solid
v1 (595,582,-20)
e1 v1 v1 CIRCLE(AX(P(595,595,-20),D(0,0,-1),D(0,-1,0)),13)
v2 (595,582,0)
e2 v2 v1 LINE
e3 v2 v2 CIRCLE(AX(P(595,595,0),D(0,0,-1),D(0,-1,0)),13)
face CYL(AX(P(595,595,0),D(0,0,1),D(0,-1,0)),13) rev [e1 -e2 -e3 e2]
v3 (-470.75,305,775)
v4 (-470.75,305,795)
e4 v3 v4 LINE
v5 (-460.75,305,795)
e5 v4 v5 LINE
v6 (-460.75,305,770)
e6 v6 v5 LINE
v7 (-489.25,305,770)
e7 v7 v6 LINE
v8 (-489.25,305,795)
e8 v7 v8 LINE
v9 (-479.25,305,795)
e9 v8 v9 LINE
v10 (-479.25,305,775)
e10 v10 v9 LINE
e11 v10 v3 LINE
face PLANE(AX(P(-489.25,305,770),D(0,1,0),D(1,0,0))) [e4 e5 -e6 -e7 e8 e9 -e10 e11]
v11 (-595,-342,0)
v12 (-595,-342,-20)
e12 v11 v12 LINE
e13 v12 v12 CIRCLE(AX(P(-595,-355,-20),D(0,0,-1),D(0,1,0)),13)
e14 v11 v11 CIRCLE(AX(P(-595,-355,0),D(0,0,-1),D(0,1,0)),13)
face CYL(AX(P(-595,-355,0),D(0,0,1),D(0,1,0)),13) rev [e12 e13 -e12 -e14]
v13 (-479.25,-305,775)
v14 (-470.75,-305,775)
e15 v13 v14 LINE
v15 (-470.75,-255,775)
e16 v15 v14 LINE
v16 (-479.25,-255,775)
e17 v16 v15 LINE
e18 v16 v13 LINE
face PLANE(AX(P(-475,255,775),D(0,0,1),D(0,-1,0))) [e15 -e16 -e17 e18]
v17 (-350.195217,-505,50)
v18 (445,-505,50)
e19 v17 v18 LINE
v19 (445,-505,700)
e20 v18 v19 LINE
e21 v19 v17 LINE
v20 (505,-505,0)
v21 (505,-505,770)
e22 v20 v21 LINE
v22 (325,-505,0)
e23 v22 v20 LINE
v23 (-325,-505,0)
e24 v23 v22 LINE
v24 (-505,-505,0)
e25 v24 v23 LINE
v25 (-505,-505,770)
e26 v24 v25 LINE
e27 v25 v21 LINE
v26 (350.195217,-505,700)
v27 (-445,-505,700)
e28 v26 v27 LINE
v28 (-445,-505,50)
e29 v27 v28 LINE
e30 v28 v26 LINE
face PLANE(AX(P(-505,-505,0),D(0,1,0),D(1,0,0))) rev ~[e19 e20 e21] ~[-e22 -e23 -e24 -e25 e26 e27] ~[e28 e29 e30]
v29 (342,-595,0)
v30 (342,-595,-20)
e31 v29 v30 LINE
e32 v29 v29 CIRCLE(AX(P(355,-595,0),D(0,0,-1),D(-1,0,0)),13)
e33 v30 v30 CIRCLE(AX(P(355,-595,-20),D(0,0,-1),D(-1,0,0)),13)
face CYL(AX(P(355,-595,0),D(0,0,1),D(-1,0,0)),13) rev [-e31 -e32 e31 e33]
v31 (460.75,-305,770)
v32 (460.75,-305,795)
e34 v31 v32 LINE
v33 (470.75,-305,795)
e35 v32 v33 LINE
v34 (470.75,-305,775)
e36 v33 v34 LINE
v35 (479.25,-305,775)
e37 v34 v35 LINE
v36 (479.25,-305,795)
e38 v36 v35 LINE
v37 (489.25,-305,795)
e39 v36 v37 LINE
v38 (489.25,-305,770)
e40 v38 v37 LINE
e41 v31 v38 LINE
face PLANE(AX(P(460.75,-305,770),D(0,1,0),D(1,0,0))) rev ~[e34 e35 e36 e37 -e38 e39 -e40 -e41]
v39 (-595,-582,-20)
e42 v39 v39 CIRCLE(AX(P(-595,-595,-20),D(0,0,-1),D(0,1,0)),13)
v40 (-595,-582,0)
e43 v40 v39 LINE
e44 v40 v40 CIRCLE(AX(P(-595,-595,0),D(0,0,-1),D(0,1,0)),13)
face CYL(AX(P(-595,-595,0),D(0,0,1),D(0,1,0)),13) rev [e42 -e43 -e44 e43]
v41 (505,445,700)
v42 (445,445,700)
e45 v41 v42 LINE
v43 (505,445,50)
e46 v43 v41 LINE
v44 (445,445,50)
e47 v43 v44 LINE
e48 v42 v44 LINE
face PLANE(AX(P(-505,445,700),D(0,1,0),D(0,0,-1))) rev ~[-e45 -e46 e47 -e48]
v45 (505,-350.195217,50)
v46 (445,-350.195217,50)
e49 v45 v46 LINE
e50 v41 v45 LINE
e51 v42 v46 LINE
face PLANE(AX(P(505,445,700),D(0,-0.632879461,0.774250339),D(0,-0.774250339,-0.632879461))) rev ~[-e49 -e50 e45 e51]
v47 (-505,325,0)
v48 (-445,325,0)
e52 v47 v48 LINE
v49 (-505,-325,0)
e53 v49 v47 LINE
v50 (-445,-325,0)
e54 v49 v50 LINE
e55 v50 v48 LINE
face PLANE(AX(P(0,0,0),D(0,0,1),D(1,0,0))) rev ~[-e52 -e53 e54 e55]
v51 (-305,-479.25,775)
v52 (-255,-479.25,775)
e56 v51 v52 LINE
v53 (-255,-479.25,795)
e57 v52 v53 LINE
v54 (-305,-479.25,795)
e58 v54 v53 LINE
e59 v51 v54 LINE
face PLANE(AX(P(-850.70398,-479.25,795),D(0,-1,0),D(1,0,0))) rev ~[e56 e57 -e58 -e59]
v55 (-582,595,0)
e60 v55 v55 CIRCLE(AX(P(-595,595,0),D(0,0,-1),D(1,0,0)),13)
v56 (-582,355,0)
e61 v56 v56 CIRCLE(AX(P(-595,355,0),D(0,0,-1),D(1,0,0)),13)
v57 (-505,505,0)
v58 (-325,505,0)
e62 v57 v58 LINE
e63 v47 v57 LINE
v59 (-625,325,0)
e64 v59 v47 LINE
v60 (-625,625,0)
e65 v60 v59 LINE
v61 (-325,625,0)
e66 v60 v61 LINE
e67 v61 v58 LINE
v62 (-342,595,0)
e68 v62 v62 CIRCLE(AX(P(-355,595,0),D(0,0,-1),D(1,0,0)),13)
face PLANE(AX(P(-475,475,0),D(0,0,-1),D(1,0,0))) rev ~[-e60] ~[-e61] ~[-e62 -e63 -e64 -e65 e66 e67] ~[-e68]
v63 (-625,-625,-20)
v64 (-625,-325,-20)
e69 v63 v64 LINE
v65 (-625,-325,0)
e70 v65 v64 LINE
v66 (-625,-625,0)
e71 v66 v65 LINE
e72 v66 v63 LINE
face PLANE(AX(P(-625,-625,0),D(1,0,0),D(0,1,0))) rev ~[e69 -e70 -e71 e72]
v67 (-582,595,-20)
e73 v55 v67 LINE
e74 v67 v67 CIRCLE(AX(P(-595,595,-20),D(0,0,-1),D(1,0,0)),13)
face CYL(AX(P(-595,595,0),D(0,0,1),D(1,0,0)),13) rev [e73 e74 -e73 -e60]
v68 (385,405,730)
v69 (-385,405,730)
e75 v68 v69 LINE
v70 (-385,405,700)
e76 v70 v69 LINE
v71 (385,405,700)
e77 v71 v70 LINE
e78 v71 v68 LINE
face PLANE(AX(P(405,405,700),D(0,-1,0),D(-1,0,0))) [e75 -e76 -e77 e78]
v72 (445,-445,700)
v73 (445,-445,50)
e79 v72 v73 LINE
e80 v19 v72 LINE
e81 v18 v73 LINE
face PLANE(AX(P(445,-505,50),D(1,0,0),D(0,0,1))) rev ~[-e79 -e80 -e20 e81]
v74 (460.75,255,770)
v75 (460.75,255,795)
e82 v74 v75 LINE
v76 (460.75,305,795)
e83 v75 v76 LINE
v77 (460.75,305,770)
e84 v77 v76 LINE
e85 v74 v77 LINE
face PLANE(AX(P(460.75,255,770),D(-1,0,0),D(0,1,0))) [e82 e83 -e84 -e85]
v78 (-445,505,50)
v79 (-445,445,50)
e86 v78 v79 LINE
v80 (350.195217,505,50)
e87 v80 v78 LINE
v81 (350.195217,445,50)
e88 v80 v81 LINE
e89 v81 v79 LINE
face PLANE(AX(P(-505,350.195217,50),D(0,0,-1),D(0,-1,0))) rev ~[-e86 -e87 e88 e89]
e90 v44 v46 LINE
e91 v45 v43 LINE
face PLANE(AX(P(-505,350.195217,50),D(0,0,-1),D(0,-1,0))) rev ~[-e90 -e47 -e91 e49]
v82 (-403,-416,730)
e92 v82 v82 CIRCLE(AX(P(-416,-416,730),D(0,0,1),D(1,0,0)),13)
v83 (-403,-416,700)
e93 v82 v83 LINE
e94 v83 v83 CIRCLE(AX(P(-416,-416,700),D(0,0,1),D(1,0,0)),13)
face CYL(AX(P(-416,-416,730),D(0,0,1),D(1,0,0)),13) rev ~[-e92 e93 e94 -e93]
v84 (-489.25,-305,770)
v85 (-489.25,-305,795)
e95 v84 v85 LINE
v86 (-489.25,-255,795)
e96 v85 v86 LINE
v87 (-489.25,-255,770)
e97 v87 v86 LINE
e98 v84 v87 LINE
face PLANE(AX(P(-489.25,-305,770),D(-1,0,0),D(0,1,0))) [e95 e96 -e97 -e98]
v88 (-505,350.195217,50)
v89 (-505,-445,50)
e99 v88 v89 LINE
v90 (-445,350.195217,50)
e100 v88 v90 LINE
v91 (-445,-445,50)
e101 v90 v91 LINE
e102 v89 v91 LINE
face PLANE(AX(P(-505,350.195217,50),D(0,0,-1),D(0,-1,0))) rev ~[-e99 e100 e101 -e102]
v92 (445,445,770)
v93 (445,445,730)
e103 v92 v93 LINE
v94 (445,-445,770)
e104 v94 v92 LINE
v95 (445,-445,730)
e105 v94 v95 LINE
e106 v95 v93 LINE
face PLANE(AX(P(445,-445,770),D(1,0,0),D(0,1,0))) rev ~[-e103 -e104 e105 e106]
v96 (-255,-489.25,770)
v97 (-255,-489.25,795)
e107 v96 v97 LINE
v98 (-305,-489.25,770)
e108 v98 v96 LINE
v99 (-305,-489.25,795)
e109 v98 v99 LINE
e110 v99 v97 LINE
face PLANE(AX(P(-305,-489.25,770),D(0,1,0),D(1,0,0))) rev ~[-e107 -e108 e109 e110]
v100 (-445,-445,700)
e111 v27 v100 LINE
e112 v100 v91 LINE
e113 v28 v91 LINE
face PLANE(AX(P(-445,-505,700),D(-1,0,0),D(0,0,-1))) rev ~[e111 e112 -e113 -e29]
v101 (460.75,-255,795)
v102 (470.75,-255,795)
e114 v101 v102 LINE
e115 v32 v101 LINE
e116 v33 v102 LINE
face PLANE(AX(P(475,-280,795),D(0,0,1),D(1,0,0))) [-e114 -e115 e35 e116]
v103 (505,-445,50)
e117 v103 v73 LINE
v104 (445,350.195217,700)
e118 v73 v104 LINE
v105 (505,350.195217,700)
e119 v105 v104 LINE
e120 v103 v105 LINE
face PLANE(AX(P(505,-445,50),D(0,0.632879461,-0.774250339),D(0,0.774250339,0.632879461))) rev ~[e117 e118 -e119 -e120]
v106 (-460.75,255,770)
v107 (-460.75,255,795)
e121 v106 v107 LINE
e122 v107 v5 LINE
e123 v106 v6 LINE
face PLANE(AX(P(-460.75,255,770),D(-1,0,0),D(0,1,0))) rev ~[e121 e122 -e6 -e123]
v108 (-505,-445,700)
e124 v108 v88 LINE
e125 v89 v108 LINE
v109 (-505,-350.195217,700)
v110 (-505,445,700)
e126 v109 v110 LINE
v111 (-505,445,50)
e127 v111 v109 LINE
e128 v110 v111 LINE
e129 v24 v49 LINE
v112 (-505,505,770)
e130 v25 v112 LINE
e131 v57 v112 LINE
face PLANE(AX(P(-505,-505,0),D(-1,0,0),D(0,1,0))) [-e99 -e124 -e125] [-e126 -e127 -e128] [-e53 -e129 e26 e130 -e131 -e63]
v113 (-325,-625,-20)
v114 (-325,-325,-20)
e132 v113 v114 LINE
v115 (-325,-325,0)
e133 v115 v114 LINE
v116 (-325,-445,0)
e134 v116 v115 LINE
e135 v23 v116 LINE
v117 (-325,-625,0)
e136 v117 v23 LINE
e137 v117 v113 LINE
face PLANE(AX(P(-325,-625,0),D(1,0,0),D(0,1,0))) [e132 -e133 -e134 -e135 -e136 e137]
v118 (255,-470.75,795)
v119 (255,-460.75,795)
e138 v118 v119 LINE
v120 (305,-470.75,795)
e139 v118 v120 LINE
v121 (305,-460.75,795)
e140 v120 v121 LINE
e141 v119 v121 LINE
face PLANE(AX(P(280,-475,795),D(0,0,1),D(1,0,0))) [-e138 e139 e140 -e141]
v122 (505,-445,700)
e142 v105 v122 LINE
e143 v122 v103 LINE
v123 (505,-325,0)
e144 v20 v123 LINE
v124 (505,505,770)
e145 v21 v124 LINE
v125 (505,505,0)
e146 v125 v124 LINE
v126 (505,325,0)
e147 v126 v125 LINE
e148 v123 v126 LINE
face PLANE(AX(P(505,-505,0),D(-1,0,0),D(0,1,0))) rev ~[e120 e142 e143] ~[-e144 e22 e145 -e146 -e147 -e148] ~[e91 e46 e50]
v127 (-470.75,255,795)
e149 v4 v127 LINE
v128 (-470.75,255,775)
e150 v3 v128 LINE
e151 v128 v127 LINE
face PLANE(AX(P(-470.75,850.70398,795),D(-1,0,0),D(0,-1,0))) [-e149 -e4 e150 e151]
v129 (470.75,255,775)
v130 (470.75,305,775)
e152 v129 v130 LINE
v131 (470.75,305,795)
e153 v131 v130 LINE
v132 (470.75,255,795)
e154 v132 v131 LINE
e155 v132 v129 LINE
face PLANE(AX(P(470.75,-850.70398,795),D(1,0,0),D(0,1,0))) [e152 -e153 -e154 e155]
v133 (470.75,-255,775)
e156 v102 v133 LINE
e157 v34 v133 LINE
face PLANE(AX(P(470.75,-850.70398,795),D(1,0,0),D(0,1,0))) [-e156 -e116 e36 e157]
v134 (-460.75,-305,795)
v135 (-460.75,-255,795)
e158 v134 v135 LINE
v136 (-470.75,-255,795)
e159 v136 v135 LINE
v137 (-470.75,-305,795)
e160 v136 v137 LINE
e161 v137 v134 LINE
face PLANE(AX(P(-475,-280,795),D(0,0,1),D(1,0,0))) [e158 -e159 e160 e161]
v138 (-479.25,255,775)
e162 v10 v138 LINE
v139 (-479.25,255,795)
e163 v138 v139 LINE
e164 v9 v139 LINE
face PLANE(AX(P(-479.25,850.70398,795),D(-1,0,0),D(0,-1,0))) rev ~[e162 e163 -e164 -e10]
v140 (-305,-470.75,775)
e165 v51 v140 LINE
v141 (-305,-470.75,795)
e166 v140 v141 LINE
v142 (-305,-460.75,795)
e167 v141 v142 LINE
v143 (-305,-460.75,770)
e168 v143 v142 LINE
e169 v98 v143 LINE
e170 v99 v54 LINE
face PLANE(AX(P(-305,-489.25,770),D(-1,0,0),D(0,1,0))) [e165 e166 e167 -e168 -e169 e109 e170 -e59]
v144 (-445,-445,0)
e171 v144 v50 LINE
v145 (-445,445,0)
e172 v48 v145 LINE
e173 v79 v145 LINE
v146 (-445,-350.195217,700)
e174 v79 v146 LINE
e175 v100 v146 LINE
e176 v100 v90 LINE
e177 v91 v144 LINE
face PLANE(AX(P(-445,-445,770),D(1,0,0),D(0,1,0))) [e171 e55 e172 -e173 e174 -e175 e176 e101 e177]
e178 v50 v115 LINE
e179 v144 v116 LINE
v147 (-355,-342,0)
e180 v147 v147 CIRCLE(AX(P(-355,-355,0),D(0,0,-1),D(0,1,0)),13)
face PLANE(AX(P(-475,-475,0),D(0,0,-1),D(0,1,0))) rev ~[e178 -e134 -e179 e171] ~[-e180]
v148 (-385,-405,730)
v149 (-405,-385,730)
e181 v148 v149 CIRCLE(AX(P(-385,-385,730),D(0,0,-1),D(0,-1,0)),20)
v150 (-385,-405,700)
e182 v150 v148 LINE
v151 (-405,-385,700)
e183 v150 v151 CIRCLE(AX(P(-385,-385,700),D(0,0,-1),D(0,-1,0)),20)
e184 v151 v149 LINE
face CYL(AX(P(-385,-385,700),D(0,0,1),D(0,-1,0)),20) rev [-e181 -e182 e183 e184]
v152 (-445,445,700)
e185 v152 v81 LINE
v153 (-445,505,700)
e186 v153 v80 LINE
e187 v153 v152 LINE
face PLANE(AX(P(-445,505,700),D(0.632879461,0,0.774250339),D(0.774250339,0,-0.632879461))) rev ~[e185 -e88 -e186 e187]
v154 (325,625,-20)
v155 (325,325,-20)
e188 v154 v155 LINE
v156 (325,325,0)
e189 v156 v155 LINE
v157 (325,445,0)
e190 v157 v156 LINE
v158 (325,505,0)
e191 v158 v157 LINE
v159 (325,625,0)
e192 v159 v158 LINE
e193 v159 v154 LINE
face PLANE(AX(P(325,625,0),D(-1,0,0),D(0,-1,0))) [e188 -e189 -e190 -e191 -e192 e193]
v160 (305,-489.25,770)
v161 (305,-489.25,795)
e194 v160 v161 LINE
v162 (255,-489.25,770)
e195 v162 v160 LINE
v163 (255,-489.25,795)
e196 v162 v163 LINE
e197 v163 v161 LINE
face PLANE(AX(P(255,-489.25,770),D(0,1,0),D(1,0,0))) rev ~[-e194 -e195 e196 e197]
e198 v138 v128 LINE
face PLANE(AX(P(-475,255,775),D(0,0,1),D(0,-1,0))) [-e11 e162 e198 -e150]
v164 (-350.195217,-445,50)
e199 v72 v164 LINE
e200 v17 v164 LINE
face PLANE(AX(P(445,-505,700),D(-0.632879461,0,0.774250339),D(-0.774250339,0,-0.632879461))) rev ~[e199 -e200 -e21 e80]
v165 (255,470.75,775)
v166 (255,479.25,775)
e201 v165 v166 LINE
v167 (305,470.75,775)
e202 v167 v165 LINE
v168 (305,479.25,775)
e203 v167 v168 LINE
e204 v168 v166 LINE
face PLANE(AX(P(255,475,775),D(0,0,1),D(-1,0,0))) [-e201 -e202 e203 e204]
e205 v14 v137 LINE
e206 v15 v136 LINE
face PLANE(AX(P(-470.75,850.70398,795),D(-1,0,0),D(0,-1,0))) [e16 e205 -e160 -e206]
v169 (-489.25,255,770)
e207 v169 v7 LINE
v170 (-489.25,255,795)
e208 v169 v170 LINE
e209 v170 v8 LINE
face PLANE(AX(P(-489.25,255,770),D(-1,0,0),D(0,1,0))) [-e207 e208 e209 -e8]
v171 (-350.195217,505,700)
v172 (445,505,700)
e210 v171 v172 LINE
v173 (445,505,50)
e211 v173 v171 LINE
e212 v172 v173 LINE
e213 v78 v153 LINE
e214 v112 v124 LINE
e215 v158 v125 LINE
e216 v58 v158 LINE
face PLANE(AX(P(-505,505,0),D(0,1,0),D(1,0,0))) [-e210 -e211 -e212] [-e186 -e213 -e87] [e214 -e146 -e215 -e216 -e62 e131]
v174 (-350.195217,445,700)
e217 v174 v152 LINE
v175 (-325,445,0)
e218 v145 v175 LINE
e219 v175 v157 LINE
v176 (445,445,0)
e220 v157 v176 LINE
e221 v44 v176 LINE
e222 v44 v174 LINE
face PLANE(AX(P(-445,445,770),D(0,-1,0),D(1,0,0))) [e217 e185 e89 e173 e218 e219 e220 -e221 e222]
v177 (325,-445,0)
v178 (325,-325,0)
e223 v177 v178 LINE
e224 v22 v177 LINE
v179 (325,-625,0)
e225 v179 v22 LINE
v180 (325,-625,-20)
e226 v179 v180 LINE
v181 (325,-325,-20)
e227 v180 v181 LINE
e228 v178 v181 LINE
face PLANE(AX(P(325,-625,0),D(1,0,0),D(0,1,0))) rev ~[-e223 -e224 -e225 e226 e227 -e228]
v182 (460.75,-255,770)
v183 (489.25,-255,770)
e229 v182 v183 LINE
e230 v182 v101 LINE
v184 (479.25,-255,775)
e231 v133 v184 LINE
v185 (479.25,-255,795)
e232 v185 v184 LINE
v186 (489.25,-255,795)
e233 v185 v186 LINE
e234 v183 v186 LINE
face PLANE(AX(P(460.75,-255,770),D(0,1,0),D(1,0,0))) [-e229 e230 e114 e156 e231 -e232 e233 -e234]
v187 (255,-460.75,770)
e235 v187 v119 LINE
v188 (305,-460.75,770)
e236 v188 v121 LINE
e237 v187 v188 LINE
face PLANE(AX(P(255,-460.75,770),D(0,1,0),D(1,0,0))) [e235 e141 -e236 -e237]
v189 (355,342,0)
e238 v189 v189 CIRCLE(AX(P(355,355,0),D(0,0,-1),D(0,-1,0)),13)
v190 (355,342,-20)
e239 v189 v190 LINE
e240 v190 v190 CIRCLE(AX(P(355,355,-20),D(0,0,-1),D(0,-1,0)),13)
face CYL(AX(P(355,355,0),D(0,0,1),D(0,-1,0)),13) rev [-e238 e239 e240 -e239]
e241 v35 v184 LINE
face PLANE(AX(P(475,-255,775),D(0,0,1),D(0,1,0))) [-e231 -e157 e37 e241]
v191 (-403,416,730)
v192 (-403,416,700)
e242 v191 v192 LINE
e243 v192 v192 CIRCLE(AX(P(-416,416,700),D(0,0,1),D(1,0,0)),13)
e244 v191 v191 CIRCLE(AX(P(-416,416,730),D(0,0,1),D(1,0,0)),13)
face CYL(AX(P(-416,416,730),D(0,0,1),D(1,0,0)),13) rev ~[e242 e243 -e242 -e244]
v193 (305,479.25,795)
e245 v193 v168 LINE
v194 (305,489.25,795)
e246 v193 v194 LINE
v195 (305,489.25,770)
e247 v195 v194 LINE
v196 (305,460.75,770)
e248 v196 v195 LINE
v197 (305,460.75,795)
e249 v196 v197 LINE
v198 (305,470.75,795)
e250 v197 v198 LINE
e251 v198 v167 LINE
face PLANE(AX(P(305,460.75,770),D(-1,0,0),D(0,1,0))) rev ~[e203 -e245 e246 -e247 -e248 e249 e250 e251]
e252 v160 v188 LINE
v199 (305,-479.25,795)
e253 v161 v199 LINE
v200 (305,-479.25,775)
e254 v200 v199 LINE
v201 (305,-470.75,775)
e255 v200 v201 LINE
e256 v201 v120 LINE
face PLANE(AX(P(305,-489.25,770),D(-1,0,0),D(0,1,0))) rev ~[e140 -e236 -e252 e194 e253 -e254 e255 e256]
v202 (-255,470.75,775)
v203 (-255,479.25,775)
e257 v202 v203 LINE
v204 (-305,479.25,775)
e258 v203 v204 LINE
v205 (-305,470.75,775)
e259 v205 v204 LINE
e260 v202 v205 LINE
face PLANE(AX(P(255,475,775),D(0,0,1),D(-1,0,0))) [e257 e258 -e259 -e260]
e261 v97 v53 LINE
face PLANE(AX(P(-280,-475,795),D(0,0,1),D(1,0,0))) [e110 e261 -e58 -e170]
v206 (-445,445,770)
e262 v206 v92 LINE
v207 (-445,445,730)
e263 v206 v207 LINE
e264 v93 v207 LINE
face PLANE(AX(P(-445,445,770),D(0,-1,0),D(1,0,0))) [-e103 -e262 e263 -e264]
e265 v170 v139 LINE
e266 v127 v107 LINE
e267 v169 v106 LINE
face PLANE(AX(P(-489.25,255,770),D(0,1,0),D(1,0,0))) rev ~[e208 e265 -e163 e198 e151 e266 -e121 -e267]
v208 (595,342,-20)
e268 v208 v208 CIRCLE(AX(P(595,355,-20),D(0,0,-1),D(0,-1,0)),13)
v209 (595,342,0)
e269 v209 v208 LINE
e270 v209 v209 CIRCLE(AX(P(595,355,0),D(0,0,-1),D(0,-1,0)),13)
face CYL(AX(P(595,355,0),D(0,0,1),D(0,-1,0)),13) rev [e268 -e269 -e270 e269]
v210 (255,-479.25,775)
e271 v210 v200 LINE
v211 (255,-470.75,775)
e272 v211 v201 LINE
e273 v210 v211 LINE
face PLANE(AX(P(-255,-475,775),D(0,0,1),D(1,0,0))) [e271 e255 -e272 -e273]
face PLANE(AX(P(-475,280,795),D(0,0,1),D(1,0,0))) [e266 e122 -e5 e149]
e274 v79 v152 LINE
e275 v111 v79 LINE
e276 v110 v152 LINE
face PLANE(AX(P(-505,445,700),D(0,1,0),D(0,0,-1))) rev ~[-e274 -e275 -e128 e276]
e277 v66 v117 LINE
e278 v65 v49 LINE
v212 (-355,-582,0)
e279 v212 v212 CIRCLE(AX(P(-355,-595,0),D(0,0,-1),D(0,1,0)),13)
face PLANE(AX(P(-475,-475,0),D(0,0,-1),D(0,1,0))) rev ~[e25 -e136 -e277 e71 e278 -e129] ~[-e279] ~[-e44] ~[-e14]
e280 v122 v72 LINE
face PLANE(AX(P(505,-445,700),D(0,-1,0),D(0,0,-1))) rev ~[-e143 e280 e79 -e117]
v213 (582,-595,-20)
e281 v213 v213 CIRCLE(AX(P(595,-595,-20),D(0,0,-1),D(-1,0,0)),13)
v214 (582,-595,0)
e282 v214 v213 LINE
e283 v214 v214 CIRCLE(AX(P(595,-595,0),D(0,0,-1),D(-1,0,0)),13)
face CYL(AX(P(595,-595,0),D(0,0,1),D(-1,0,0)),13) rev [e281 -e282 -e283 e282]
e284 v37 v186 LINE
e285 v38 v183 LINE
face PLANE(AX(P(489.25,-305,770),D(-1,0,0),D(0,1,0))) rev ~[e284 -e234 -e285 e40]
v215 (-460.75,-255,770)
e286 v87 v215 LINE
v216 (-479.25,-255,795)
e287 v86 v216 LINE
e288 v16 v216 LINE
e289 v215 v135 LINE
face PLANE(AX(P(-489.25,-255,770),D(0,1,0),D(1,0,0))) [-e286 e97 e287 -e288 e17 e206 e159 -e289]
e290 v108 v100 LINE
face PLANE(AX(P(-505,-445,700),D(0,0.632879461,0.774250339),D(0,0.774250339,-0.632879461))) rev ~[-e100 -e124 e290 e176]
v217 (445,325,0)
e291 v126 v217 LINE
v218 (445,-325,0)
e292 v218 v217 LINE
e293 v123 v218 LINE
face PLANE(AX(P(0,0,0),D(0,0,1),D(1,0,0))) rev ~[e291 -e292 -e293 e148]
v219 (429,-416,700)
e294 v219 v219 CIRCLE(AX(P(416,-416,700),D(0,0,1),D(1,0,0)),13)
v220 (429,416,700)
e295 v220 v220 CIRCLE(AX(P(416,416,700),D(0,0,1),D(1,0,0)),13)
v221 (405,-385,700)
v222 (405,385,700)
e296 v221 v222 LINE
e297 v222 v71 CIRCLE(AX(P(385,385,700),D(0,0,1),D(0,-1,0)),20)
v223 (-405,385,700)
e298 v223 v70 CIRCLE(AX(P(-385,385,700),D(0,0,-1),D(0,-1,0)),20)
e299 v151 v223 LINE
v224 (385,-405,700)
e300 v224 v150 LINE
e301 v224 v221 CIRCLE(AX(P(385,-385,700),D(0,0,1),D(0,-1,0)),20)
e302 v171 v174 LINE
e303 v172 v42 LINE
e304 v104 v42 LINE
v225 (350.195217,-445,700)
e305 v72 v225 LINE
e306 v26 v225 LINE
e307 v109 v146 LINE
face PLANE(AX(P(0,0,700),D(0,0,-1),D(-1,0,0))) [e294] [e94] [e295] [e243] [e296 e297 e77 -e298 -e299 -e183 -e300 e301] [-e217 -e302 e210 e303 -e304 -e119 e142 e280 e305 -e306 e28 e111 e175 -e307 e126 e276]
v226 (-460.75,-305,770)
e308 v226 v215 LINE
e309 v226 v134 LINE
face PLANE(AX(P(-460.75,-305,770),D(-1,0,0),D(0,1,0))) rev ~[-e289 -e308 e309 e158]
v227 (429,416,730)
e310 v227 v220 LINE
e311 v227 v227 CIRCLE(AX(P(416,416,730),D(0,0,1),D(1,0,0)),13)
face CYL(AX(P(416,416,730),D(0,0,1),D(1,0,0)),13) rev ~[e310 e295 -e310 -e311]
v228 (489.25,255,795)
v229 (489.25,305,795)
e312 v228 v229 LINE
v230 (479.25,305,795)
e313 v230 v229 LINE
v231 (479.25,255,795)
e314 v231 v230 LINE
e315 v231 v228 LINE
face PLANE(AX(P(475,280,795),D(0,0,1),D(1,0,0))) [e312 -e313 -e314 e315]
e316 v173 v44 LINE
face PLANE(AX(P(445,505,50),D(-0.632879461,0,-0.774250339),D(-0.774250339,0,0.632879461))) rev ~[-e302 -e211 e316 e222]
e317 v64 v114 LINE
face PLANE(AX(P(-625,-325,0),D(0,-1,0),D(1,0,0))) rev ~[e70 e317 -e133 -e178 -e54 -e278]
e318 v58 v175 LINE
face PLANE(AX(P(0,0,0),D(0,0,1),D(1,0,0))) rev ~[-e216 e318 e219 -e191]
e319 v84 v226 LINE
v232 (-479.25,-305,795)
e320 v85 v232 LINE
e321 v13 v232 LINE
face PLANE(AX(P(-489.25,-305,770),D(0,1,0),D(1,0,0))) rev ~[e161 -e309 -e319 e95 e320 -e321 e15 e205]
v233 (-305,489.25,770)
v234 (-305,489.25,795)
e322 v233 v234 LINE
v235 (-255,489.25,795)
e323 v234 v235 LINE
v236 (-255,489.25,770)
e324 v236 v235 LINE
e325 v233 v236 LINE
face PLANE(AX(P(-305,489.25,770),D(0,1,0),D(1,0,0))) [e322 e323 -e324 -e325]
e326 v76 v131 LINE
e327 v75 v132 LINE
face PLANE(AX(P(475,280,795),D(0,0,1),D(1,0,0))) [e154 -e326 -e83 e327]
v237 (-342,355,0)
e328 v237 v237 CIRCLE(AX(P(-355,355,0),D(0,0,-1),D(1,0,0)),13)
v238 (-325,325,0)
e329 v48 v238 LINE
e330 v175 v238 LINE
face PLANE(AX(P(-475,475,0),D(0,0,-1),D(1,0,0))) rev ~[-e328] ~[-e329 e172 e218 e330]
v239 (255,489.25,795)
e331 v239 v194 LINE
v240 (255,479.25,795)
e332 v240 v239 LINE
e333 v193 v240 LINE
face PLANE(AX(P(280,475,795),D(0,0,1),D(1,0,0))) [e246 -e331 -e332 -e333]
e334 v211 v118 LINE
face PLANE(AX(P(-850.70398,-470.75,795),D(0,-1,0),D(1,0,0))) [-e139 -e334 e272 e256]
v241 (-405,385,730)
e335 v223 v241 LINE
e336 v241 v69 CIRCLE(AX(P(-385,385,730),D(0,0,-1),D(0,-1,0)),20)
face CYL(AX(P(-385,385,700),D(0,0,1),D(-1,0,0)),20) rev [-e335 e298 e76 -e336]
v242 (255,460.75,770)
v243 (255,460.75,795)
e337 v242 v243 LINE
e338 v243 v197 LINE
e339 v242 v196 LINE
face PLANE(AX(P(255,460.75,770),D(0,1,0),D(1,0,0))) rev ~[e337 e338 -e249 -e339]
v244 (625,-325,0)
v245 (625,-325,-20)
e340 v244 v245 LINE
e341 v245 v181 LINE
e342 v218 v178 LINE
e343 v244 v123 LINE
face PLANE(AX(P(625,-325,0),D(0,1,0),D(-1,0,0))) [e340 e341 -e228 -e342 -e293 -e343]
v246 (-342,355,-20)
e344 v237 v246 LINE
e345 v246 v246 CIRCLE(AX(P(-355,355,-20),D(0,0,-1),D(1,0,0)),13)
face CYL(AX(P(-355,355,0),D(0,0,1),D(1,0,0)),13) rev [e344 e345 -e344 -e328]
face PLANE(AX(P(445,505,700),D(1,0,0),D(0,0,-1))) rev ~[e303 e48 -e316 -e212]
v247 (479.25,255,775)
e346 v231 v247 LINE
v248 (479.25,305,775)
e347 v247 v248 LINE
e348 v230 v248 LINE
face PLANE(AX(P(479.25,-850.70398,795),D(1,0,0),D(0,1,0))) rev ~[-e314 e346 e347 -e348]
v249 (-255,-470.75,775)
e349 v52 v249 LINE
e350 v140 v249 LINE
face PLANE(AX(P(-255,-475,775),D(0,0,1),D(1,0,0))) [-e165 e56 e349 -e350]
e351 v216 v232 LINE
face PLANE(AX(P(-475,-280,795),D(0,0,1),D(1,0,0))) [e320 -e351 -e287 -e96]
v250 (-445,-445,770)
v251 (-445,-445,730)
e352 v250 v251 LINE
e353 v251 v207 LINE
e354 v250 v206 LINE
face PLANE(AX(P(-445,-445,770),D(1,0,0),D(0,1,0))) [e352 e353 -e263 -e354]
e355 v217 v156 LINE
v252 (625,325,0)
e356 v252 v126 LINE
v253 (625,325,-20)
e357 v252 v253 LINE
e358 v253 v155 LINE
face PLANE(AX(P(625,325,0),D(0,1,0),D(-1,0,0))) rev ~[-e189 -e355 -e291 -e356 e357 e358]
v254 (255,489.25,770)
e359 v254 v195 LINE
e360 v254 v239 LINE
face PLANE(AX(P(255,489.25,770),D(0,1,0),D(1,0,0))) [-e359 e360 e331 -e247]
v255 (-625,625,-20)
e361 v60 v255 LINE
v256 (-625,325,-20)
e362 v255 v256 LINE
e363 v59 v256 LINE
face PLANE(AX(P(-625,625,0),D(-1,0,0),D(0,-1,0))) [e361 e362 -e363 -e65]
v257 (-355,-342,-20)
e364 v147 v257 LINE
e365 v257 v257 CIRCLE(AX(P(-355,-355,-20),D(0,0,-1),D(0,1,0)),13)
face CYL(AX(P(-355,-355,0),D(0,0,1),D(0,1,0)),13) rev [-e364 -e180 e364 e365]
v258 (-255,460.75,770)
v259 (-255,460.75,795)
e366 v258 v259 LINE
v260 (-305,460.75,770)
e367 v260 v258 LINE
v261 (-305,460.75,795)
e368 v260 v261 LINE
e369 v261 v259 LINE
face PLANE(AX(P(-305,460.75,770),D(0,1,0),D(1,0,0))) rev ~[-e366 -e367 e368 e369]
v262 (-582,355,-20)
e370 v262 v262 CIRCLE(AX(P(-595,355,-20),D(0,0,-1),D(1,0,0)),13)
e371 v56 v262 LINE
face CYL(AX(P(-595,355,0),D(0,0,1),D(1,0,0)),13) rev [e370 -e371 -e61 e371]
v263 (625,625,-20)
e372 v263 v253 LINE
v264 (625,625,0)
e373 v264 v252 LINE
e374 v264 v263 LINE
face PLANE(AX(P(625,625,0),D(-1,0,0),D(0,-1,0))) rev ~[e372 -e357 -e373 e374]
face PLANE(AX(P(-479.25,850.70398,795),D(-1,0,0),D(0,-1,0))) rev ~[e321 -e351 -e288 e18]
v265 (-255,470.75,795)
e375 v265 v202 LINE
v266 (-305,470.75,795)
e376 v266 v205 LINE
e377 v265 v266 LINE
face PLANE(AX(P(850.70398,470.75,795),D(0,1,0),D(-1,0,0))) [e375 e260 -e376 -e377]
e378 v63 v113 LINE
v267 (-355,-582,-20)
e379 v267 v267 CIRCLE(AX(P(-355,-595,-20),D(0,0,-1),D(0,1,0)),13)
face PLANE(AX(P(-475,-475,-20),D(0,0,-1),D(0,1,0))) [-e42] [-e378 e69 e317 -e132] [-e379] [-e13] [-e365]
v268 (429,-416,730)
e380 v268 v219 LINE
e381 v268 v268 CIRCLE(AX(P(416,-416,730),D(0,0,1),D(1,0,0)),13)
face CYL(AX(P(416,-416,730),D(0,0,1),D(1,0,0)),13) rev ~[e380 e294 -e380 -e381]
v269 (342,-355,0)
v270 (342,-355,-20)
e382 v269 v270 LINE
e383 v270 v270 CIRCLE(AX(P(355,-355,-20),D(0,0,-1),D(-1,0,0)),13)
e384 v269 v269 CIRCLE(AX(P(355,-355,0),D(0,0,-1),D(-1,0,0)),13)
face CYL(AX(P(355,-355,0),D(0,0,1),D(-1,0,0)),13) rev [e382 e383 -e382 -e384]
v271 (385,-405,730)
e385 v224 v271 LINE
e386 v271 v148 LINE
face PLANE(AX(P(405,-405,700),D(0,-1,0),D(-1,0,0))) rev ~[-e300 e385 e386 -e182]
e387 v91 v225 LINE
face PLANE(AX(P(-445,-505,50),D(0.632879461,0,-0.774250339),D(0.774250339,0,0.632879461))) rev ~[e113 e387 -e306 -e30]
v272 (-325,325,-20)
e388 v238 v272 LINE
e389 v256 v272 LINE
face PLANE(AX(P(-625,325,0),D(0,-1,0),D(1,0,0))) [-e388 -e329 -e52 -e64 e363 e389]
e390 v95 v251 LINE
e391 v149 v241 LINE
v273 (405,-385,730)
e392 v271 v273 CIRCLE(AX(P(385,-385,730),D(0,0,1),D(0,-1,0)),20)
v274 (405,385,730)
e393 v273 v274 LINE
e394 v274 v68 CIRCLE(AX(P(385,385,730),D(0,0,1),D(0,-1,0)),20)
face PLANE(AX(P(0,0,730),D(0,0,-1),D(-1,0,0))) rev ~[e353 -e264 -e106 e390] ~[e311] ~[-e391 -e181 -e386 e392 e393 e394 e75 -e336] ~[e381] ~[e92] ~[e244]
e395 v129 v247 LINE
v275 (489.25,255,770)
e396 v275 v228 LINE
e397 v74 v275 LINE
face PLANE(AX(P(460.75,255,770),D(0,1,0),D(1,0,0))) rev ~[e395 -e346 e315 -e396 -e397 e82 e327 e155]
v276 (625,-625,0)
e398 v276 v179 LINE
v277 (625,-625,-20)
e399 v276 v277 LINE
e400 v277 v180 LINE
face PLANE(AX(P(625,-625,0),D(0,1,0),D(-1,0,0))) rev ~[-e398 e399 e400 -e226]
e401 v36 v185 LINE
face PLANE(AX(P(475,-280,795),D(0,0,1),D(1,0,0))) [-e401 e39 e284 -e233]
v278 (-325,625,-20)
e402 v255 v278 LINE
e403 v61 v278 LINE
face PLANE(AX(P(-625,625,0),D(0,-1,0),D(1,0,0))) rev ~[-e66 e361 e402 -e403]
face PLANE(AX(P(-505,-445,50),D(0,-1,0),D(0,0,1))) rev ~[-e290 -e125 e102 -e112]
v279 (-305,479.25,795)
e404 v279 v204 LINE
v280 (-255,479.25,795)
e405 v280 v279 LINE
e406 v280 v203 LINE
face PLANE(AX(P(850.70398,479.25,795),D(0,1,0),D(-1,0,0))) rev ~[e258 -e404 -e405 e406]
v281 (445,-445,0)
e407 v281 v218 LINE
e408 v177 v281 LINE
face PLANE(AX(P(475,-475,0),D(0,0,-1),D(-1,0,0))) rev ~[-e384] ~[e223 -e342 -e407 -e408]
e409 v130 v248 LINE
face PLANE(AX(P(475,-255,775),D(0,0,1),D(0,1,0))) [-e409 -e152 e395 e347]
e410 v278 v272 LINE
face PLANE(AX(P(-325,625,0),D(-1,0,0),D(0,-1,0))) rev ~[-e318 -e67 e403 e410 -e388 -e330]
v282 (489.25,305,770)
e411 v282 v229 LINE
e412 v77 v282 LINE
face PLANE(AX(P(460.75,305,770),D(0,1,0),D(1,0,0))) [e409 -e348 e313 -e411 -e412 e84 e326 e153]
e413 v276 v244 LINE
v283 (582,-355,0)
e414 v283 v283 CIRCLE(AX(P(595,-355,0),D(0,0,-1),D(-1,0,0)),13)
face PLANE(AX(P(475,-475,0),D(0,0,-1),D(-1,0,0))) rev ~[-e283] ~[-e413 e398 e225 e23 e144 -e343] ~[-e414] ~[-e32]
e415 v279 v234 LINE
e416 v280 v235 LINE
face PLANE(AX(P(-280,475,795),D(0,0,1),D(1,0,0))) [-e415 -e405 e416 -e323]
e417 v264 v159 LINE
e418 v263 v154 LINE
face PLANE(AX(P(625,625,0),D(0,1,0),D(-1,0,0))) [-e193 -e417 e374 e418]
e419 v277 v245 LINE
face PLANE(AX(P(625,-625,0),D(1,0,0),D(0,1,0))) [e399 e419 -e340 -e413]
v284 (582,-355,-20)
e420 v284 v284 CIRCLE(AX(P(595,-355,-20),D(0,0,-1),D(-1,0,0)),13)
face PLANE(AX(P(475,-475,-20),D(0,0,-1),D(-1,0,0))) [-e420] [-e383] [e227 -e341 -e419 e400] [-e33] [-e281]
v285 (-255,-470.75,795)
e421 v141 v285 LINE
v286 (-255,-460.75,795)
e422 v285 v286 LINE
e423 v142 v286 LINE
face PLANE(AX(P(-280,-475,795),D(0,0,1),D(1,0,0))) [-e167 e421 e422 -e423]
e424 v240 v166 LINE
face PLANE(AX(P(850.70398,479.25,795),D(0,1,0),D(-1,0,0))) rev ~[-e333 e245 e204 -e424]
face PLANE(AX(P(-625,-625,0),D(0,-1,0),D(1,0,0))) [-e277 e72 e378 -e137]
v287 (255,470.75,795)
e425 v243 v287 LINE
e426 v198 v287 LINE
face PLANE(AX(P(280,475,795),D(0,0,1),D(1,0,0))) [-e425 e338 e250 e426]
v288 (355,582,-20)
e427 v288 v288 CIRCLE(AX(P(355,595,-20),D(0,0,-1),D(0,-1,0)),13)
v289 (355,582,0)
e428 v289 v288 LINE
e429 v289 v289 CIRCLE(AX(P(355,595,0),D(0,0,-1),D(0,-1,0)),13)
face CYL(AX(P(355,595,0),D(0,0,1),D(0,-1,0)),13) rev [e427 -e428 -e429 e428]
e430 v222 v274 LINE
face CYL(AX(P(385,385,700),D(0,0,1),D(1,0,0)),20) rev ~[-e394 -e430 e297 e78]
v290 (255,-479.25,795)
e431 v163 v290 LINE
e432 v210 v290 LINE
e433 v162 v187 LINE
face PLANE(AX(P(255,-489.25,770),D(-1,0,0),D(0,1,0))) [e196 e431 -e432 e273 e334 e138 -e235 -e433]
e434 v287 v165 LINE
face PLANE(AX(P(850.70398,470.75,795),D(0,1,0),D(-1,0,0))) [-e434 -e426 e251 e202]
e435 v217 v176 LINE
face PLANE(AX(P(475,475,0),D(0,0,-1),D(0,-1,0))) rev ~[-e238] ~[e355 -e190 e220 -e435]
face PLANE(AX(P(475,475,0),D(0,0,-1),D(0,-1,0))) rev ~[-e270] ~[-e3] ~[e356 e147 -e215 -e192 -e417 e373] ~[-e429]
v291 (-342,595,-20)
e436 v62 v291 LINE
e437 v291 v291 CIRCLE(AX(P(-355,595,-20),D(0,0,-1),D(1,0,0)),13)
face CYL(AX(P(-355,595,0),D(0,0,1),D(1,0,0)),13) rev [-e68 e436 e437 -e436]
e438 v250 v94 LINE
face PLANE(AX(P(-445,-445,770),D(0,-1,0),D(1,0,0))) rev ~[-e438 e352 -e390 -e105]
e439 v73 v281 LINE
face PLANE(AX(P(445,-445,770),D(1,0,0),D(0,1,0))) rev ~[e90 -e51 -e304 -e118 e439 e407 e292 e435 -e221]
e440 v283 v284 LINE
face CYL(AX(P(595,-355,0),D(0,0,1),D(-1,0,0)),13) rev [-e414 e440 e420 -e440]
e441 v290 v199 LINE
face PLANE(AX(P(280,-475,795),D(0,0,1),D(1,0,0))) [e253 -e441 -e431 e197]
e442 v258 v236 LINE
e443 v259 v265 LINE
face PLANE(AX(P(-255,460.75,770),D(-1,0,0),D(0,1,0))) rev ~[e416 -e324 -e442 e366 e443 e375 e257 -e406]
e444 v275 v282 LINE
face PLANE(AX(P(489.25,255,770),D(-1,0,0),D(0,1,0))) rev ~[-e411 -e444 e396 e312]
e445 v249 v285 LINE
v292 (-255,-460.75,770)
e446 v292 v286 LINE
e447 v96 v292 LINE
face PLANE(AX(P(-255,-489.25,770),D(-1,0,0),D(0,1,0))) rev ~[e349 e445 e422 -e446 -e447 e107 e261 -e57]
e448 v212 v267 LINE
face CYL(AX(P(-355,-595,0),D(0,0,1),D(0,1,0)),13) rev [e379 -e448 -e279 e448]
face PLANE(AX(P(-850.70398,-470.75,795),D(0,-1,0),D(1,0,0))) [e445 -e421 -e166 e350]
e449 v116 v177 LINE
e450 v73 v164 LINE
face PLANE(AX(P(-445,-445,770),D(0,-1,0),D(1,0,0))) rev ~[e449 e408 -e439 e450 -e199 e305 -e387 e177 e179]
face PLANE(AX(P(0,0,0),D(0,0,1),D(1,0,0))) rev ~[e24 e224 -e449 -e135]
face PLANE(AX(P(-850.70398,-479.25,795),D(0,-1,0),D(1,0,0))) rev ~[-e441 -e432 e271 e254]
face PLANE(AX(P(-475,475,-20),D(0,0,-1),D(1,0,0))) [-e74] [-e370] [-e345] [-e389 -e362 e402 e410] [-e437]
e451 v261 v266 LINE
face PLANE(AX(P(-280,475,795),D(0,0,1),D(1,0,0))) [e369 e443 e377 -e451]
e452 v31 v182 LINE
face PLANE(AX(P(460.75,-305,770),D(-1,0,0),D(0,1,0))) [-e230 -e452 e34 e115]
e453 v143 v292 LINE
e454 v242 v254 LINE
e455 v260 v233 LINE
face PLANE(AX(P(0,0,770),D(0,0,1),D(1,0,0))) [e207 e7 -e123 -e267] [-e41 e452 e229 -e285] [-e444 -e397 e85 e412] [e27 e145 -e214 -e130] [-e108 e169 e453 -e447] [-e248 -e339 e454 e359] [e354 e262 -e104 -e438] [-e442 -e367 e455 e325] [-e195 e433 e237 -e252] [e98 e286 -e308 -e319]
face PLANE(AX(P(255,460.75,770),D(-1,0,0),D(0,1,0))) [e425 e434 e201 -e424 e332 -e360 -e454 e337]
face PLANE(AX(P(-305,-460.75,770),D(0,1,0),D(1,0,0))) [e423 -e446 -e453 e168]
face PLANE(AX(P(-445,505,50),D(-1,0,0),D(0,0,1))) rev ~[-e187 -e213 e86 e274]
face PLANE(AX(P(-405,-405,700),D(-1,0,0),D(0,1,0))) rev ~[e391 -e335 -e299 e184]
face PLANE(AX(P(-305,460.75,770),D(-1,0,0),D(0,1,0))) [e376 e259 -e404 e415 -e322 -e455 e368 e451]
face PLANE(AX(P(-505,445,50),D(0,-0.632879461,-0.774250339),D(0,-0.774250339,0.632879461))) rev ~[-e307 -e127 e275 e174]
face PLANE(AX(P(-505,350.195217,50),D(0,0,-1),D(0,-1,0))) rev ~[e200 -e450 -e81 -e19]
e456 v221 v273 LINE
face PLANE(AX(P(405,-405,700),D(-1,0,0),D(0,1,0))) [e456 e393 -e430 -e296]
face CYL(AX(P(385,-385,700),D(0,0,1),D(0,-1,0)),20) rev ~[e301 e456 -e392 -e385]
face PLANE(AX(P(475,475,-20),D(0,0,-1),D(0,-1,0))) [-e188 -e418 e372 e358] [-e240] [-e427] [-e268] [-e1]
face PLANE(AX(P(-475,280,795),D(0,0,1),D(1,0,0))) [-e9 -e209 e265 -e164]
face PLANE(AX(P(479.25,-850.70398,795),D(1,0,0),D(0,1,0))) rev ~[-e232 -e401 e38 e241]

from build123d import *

# Parameters (mm, degrees)
SKETCH1_W           = 1010
SKETCH1_H           = 1010
BOSS_EXTRUDE1_DEPTH = 770
SKETCH2_W           = 890
SKETCH2_H           = 650
CUT_EXTRUDE1_DEPTH  = 445
CUT_EXTRUDE2_DEPTH  = 60
CIRPATTERN2_COUNT   = 4
SKETCH5_W           = 890
SKETCH5_H           = 890
CUT_EXTRUDE3_DEPTH  = 1065
SKETCH6_W           = 890
SKETCH6_H           = 890
SKETCH6_W_2         = 810
SKETCH6_H_2         = 810
BOSS_EXTRUDE2_DEPTH = 30
FILLET1_R           = 20
SKETCH7_R           = 13
CUT_EXTRUDE4_DEPTH  = 30
SKETCH8_W           = 300
SKETCH8_H           = 300
SKETCH8_R           = 13
BOSS_EXTRUDE3_DEPTH = 20
CIRPATTERN3_COUNT   = 4
SKETCH9_W           = 50
SKETCH9_H           = 28.5
SKETCH9_W_2         = 28.5
SKETCH9_H_2         = 50
BOSS_EXTRUDE4_DEPTH = 25
SKETCH10_W          = 1191.407960266
SKETCH10_H          = 8.5
CUT_EXTRUDE5_DEPTH  = 20
CIRPATTERN4_COUNT   = 4


with BuildPart() as part:
    # Sketch1 → Boss-Extrude1 (new body)
    with BuildSketch(Plane.XY):
        Rectangle(SKETCH1_W, SKETCH1_H)
    extrude(amount=BOSS_EXTRUDE1_DEPTH)

    # Sketch2 → Cut-Extrude1 (cut, symmetric)
    with BuildSketch(Plane(origin=(0, 0, 0), x_dir=(1, 0, 0), z_dir=(0, 1, 0))):
        with Locations((0, -375)):
            Rectangle(SKETCH2_W, SKETCH2_H)
    extrude(amount=CUT_EXTRUDE1_DEPTH, both=True, mode=Mode.SUBTRACT)

    # Sketch3 → Cut-Extrude2 (cut)
    with BuildSketch(Plane.ZY.offset(505)):
        Polygon((700, -350.195216969), (700, 445), (50, 445), align=None)
        Polygon((50, 350.195216969), (50, -445), (700, -445), align=None)
    cut_extrude2 = extrude(amount=-CUT_EXTRUDE2_DEPTH, mode=Mode.SUBTRACT)

    # CirPattern2: Cut-Extrude2 ×4 about axis
    cirpattern2_axis = Axis((0, 0, 0), (0, 0, 1))
    for i in range(1, CIRPATTERN2_COUNT):
        add(cut_extrude2.rotate(cirpattern2_axis, i * 360 / CIRPATTERN2_COUNT), mode=Mode.SUBTRACT)

    # Sketch5 → Cut-Extrude3 (cut)
    with BuildSketch(Plane.XY.offset(770)):
        Rectangle(SKETCH5_W, SKETCH5_H)
    extrude(amount=-CUT_EXTRUDE3_DEPTH, mode=Mode.SUBTRACT)

    # Sketch6 → Boss-Extrude2 (add)
    with BuildSketch(Plane(origin=(0, 0, 700), x_dir=(-1, 0, 0), z_dir=(0, 0, -1))):
        Rectangle(SKETCH6_W, SKETCH6_H)
        Rectangle(SKETCH6_W_2, SKETCH6_H_2, mode=Mode.SUBTRACT)
    extrude(amount=-BOSS_EXTRUDE2_DEPTH)

    # Fillet1
    fillet1_edges = [part.edges().sort_by_distance(p)[0] for p in [
        (405, 405, 715),
        (-405, 405, 715),
        (-405, -405, 715),
        (405, -405, 715),
    ]]
    fillet(fillet1_edges, radius=FILLET1_R)

    # Sketch7 → Cut-Extrude4 (cut)
    with BuildSketch(Plane.XY.offset(730)):
        with Locations((-416, 416)):
            Circle(SKETCH7_R)
        with Locations((416, 416)):
            Circle(SKETCH7_R)
        with Locations((416, -416)):
            Circle(SKETCH7_R)
        with Locations((-416, -416)):
            Circle(SKETCH7_R)
    extrude(amount=-CUT_EXTRUDE4_DEPTH, mode=Mode.SUBTRACT)

    # Sketch8 → Boss-Extrude3 (add)
    with BuildSketch(Plane(origin=(0, 0, 0), x_dir=(-1, 0, 0), z_dir=(0, 0, -1))):
        with Locations((-475, -475)):
            Rectangle(SKETCH8_W, SKETCH8_H)
        with Locations((-595, -355)):
            Circle(SKETCH8_R, mode=Mode.SUBTRACT)
        with Locations((-355, -355)):
            Circle(SKETCH8_R, mode=Mode.SUBTRACT)
        with Locations((-595, -595)):
            Circle(SKETCH8_R, mode=Mode.SUBTRACT)
        with Locations((-355, -595)):
            Circle(SKETCH8_R, mode=Mode.SUBTRACT)
    boss_extrude3 = extrude(amount=BOSS_EXTRUDE3_DEPTH)

    # CirPattern3: Boss-Extrude3 ×4 about axis
    cirpattern3_axis = Axis((0, 0, 0), (0, 0, 1))
    for i in range(1, CIRPATTERN3_COUNT):
        add(boss_extrude3.rotate(cirpattern3_axis, i * 360 / CIRPATTERN3_COUNT))

    # Sketch9 → Boss-Extrude4 (add)
    with BuildSketch(Plane.XY.offset(770)):
        with Locations((-280, -475)):
            Rectangle(SKETCH9_W, SKETCH9_H)
        with Locations((280, -475)):
            Rectangle(SKETCH9_W, SKETCH9_H)
        with Locations((-475, 280)):
            Rectangle(SKETCH9_W_2, SKETCH9_H_2)
        with Locations((-475, -280)):
            Rectangle(SKETCH9_W_2, SKETCH9_H_2)
        with Locations((280, 475)):
            Rectangle(SKETCH9_W, SKETCH9_H)
        with Locations((-280, 475)):
            Rectangle(SKETCH9_W, SKETCH9_H)
        with Locations((475, -280)):
            Rectangle(SKETCH9_W_2, SKETCH9_H_2)
        with Locations((475, 280)):
            Rectangle(SKETCH9_W_2, SKETCH9_H_2)
    extrude(amount=BOSS_EXTRUDE4_DEPTH)

    # Sketch10 → Cut-Extrude5 (cut)
    with BuildSketch(Plane.XY.offset(795)):
        with Locations((-255, -475)):
            Rectangle(SKETCH10_W, SKETCH10_H)
    cut_extrude5 = extrude(amount=-CUT_EXTRUDE5_DEPTH, mode=Mode.SUBTRACT)

    # CirPattern4: Cut-Extrude5 ×4 about axis
    cirpattern4_axis = Axis((0, 0, 0), (0, 0, 1))
    for i in range(1, CIRPATTERN4_COUNT):
        add(cut_extrude5.rotate(cirpattern4_axis, i * 360 / CIRPATTERN4_COUNT), mode=Mode.SUBTRACT)


solid = part.part
